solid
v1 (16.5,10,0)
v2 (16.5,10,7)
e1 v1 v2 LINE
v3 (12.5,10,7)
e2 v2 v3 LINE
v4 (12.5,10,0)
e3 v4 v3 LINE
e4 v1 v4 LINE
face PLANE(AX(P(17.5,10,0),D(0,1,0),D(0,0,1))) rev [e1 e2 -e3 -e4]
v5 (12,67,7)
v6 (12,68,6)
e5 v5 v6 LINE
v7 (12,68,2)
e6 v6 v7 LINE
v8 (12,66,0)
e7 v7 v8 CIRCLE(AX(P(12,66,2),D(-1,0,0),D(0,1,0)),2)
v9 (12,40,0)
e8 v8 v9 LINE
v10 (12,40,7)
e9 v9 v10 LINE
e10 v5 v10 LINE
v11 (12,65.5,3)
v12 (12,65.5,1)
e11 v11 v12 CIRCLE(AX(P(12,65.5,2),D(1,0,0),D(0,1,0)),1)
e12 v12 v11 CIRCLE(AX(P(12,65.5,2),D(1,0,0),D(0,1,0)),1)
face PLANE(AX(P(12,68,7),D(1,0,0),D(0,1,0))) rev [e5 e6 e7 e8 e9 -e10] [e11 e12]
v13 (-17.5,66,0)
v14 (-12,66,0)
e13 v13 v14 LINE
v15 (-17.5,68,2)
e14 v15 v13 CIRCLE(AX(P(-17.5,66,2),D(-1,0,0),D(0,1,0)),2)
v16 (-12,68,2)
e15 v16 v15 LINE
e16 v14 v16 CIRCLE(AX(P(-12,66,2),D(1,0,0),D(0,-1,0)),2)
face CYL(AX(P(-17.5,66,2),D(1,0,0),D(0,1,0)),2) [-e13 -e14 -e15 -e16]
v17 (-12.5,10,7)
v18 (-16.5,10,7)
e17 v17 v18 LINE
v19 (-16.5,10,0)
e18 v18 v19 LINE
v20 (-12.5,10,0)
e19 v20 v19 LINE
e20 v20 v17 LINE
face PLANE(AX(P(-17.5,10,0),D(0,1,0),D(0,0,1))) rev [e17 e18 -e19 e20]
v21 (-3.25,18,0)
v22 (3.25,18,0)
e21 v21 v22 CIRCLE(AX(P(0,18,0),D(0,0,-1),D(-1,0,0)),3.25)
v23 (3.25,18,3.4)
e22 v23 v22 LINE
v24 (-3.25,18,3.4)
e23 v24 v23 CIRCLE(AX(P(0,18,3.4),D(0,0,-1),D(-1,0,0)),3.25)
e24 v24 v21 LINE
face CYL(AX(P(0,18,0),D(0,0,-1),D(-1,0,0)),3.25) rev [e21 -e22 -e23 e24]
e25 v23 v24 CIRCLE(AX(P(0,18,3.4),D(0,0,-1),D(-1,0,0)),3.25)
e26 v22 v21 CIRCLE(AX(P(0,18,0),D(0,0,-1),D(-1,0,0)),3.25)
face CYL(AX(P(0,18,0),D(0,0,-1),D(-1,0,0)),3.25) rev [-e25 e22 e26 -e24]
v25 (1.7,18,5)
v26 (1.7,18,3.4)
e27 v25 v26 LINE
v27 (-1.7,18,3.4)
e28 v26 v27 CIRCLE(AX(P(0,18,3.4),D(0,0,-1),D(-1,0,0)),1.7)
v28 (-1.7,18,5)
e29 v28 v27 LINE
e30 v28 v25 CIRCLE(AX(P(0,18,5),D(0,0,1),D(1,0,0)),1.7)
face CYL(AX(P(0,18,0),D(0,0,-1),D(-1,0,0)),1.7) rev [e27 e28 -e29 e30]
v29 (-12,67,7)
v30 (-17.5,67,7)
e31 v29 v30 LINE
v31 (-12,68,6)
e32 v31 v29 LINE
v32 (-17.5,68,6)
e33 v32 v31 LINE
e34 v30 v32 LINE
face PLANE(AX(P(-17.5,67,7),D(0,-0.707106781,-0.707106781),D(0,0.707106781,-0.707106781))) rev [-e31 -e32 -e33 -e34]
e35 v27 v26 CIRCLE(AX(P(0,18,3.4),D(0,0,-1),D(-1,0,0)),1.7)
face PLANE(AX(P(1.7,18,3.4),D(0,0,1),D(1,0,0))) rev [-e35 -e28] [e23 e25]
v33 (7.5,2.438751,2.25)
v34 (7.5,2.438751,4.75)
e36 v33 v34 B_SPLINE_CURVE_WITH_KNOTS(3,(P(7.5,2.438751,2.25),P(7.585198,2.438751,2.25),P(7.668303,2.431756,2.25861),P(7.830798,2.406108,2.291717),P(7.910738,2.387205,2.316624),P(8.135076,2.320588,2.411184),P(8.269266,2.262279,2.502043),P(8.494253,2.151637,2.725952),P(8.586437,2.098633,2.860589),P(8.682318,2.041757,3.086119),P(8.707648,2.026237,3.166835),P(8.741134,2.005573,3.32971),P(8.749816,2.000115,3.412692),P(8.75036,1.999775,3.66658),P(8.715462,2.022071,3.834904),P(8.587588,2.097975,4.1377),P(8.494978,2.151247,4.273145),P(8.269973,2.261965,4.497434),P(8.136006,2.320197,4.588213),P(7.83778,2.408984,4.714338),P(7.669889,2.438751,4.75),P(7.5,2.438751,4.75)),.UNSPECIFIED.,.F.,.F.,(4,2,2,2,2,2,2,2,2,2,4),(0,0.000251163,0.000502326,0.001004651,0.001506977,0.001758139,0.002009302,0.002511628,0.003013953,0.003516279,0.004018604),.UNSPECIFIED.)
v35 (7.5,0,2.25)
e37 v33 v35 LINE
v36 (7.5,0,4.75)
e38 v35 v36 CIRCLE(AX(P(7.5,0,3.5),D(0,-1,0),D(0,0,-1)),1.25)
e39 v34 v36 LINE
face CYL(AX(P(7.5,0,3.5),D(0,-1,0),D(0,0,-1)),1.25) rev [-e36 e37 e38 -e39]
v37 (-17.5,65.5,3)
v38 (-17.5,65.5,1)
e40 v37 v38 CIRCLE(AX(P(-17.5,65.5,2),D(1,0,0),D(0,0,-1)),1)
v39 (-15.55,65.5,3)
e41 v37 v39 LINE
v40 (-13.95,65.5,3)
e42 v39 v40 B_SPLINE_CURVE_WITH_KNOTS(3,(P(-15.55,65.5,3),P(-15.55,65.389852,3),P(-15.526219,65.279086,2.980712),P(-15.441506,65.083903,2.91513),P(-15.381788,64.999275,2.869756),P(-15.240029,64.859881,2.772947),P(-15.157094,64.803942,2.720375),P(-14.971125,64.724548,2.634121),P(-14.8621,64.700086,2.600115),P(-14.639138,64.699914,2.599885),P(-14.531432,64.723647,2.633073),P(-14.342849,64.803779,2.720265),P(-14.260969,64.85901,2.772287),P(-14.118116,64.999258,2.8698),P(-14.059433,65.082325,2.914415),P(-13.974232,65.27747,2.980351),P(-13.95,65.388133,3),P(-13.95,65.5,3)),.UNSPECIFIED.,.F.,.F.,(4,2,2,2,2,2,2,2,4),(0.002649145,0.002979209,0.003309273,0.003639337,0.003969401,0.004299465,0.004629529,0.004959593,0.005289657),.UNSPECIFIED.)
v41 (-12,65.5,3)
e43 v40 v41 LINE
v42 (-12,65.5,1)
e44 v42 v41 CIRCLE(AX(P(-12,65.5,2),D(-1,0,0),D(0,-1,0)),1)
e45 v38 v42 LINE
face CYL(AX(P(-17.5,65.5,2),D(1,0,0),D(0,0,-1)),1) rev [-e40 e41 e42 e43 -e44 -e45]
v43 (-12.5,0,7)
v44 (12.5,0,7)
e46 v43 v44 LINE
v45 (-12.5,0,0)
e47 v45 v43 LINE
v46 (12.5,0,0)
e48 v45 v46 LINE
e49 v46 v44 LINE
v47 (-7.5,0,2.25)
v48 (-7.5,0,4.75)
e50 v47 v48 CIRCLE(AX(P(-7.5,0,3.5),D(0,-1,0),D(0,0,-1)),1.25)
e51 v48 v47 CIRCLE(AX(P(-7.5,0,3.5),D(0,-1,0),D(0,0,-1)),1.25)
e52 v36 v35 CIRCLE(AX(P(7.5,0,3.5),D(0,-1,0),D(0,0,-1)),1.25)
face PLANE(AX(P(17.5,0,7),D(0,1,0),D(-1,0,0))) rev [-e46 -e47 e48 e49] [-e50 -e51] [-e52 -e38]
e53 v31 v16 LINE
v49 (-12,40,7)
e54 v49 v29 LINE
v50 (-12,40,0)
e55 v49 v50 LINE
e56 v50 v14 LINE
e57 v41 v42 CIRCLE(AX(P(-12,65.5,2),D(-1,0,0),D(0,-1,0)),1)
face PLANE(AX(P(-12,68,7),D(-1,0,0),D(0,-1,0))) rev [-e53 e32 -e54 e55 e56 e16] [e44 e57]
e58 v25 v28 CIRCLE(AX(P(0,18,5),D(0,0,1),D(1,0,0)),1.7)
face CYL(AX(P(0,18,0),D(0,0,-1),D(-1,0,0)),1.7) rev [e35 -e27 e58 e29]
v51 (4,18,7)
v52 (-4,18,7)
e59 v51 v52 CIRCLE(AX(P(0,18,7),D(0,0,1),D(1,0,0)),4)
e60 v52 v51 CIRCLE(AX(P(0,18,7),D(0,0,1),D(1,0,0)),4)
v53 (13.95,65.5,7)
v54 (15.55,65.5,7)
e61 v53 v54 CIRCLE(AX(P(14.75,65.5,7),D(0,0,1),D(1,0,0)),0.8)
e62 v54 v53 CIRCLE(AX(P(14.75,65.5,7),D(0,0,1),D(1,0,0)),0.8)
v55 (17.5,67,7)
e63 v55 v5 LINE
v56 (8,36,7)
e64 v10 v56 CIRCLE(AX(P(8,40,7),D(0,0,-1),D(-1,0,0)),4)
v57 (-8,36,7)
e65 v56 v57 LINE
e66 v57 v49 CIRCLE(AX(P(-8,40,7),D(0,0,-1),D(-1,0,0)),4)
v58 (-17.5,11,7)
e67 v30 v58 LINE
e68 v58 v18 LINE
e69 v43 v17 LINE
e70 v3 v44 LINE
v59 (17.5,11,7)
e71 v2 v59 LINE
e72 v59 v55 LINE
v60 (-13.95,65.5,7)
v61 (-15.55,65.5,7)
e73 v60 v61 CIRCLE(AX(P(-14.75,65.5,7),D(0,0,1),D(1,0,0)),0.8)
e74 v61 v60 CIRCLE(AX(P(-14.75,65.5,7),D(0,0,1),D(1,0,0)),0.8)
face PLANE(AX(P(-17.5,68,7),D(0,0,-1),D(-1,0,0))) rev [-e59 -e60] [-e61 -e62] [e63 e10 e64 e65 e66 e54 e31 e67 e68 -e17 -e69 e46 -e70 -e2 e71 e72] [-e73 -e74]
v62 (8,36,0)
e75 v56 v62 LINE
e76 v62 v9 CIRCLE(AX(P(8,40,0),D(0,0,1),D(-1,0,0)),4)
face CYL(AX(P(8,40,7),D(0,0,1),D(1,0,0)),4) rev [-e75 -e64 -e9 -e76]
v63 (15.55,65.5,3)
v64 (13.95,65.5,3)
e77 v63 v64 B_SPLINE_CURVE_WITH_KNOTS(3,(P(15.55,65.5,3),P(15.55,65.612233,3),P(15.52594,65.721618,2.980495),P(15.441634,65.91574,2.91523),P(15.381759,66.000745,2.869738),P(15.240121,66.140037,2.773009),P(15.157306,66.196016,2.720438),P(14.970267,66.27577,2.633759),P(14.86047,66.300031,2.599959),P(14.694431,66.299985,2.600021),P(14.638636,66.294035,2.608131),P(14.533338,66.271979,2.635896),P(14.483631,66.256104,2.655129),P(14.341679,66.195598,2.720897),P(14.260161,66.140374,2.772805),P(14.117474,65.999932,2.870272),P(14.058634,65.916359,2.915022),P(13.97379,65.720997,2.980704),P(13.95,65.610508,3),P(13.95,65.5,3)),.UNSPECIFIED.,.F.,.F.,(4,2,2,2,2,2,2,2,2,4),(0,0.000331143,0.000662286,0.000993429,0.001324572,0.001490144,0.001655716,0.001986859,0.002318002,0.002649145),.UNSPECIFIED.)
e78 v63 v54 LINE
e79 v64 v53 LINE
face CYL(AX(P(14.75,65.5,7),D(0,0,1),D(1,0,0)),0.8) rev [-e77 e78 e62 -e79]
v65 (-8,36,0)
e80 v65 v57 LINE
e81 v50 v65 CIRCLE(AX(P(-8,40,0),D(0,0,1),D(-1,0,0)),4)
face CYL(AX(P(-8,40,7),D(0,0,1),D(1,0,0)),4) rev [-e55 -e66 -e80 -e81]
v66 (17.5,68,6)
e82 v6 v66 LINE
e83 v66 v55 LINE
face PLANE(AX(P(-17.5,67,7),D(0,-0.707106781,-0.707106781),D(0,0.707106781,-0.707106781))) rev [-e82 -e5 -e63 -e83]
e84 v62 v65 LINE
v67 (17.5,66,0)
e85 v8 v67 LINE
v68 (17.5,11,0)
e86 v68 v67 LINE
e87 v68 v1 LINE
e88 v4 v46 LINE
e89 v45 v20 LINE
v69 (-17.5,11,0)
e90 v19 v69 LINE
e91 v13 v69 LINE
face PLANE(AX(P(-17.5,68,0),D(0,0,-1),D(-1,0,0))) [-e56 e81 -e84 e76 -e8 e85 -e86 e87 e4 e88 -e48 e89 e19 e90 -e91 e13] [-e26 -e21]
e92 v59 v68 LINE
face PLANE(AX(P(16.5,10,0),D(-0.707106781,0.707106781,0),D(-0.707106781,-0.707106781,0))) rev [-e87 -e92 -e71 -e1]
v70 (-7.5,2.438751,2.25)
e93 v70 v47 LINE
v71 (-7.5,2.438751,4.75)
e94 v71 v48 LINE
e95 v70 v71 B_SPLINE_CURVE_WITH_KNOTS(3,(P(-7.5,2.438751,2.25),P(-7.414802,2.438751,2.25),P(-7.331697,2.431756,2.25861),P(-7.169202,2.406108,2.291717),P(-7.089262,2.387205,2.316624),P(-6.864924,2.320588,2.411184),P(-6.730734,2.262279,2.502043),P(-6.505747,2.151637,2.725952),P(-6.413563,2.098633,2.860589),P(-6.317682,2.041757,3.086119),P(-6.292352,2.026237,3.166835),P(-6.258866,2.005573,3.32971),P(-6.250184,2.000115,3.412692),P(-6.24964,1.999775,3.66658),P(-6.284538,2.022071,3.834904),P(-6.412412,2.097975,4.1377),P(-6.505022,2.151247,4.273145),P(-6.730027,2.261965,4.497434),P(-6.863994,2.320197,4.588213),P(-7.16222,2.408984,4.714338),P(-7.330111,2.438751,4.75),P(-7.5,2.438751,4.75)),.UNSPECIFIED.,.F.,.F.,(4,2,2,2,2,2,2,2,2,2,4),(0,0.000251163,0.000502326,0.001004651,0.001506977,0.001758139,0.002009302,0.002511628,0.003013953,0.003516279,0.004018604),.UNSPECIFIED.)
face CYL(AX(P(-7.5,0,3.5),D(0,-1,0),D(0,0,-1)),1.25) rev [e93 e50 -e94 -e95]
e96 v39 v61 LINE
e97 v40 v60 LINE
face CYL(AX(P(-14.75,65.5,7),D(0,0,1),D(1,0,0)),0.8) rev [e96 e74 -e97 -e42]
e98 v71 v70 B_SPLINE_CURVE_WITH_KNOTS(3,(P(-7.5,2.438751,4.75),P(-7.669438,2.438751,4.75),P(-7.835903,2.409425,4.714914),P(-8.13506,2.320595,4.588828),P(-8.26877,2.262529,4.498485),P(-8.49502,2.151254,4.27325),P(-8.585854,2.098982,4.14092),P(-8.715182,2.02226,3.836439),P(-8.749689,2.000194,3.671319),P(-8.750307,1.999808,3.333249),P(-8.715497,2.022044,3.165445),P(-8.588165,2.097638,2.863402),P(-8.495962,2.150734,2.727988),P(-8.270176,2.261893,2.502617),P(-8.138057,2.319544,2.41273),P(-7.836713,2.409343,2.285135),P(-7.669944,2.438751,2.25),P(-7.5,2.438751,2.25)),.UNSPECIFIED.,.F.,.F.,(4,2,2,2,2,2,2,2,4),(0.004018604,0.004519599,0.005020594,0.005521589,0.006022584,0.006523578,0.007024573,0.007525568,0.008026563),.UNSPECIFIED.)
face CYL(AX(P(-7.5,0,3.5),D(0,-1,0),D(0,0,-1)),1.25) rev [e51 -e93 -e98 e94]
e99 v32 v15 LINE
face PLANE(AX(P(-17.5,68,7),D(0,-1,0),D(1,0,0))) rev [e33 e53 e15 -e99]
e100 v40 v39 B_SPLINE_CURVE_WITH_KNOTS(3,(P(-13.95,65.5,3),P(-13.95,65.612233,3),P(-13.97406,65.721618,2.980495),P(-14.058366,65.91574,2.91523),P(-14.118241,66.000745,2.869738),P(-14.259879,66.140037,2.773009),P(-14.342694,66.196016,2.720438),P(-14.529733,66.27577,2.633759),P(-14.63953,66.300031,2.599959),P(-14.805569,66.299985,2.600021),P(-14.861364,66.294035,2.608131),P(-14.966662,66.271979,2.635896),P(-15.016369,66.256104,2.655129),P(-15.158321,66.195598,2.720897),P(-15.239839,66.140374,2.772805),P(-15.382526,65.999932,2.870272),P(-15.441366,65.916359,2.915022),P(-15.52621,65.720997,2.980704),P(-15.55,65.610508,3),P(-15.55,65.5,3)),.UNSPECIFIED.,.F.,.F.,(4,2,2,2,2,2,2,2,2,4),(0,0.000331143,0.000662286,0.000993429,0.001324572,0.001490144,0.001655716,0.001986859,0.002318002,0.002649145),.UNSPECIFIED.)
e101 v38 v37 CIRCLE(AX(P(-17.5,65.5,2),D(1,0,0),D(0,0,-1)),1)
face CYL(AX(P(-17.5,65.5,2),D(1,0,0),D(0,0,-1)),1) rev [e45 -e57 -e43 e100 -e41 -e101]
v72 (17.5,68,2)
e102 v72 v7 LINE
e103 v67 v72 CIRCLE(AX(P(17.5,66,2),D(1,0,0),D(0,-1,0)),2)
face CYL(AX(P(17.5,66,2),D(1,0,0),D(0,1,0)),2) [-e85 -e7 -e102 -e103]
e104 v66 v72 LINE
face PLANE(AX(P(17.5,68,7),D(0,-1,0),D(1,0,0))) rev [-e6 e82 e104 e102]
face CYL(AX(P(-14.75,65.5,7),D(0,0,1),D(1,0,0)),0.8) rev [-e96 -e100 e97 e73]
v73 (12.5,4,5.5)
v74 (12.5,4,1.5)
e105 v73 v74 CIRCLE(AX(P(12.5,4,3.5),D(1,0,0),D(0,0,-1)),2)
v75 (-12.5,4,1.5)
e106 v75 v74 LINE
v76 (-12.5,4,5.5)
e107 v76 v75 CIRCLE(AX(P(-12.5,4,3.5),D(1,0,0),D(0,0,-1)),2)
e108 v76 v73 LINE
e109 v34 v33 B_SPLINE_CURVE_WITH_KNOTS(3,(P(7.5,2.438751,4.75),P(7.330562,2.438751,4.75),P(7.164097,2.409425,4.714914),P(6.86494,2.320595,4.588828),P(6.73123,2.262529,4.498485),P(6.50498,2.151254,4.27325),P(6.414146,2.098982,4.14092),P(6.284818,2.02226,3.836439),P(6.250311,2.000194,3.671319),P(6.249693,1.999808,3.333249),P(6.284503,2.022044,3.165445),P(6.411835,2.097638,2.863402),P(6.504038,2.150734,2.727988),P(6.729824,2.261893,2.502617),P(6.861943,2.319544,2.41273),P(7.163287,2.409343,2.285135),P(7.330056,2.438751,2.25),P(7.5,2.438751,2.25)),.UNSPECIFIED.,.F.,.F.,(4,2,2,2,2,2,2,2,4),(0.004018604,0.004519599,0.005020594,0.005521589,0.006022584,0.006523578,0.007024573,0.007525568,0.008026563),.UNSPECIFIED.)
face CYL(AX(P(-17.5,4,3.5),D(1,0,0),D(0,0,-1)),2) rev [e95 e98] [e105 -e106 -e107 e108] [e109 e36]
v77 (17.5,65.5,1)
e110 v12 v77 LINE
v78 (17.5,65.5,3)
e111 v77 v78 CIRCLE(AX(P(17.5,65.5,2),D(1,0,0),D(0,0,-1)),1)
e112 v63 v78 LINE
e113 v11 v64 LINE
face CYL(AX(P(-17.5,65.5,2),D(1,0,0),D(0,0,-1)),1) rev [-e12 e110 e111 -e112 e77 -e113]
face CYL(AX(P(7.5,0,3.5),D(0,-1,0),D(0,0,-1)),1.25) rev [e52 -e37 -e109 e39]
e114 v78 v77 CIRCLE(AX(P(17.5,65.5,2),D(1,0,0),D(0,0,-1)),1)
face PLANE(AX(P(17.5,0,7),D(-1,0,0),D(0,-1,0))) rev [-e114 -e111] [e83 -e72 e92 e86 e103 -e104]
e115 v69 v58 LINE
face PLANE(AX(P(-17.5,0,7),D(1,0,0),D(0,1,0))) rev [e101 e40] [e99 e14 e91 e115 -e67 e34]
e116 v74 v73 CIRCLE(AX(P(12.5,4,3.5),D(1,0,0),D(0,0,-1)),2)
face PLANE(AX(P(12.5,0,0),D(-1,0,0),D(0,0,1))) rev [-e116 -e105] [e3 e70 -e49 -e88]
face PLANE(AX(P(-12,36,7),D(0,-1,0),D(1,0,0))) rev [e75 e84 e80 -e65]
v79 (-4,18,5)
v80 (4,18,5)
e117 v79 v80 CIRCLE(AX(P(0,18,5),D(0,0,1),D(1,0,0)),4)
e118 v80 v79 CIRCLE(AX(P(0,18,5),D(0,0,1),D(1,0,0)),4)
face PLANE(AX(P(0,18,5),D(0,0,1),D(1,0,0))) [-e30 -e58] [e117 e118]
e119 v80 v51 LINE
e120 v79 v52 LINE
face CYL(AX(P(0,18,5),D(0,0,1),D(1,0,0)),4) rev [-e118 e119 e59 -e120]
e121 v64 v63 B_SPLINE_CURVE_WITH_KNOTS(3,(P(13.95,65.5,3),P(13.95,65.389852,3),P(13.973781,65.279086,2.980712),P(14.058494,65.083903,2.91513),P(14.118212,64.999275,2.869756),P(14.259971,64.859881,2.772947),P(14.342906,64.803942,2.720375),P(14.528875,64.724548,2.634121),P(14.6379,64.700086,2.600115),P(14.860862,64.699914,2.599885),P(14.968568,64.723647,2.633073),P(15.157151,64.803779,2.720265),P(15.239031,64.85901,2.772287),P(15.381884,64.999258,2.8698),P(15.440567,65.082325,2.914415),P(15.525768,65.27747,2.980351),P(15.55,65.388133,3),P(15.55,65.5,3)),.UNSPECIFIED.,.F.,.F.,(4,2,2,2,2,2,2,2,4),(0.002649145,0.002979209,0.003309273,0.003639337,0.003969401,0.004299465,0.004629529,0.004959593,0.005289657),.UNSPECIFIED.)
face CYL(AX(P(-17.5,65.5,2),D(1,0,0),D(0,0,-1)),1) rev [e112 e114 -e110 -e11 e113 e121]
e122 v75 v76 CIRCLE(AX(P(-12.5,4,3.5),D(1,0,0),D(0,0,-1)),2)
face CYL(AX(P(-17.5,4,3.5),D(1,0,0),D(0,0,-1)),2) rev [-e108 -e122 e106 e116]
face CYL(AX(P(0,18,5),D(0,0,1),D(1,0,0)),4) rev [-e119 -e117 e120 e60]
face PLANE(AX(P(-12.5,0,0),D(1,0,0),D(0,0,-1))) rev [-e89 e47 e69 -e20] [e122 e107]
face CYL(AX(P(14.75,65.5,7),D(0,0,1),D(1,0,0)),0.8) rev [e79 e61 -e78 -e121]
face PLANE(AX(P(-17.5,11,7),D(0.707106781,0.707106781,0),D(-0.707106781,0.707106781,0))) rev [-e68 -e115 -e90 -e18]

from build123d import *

# Parameters (mm, degrees)
BOSS_EXTRUDE1_DEPTH                                 = 7
SKETCH2_R                                           = 1
CUT_EXTRUDE1_DEPTH                                  = 77.798437484
SKETCH3_W                                           = 5
SKETCH3_H                                           = 10
CUT_EXTRUDE2_DEPTH                                  = 71.563800918
SKETCH4_R                                           = 2
CUT_EXTRUDE3_DEPTH                                  = 75.652528423
M3_TAPPED_HOLE1_REACH                               = 72.564
M3_TAPPED_HOLE1_BORE_R                              = 1.25
FILLET1_R                                           = 4
CHAMFER1_SIZE                                       = 1
SKETCH8_R                                           = 4
CUT_EXTRUDE4_DEPTH                                  = 2
FILLET2_R                                           = 2
M2_TAPPED_HOLE1_D                                   = 1.6
M2_TAPPED_HOLE1_DEPTH                               = 5.2
M2_TAPPED_HOLE1_TIP                                 = 0.480688495
CBORE_FOR_M3_HEX_SOCKET_HEAD_CAP_SCREW1_D           = 3.4
CBORE_FOR_M3_HEX_SOCKET_HEAD_CAP_SCREW1_CBORE_D     = 6.5
CBORE_FOR_M3_HEX_SOCKET_HEAD_CAP_SCREW1_CBORE_DEPTH = 3.4


with BuildPart() as part:
    # Sketch1 → Boss-Extrude1 (new body)
    with BuildSketch(Plane.XY):
        Polygon((17.5, 0), (-17.5, 0), (-17.5, 68), (-12, 68), (-12, 36), (12, 36), (12, 68), (17.5, 68), align=None)
    extrude(amount=BOSS_EXTRUDE1_DEPTH)

    # Sketch2 → Cut-Extrude1 (cut, through all)
    with BuildSketch(Plane(origin=(17.5, 0, 0), x_dir=(0, 0, -1), z_dir=(1, 0, 0))):
        with Locations((-2, 65.5)):
            Circle(SKETCH2_R)
    extrude(amount=-CUT_EXTRUDE1_DEPTH, mode=Mode.SUBTRACT)

    # Sketch3 → Cut-Extrude2 (cut, through all)
    with BuildSketch(Plane.XY.offset(7)):
        with Locations((-15, 5)):
            Rectangle(SKETCH3_W, SKETCH3_H)
        with Locations((15, 5)):
            Rectangle(SKETCH3_W, SKETCH3_H)
    extrude(amount=-CUT_EXTRUDE2_DEPTH, mode=Mode.SUBTRACT)

    # Sketch4 → Cut-Extrude3 (cut, through all)
    with BuildSketch(Plane(origin=(12.5, 0, 0), x_dir=(0, 0, -1), z_dir=(1, 0, 0))):
        with Locations((-3.5, 4)):
            Circle(SKETCH4_R)
    extrude(amount=-CUT_EXTRUDE3_DEPTH, mode=Mode.SUBTRACT)

    # M3 Tapped Hole1 bore → M3 Tapped Hole1 (cut, up to next)
    with BuildSketch(Plane.XZ, mode=Mode.PRIVATE) as m3_tapped_hole1_sk1:
        with Locations((7.5, 3.5)):
            Circle(M3_TAPPED_HOLE1_BORE_R)
    m3_tapped_hole1_tool1 = extrude(m3_tapped_hole1_sk1.sketch, amount=-M3_TAPPED_HOLE1_REACH, mode=Mode.PRIVATE) & part.part
    # M3 Tapped Hole1 bore → M3 Tapped Hole1 (cut, up to next)
    with BuildSketch(Plane.XZ, mode=Mode.PRIVATE) as m3_tapped_hole1_sk2:
        with Locations((-7.5, 3.5)):
            Circle(M3_TAPPED_HOLE1_BORE_R)
    m3_tapped_hole1_tool2 = extrude(m3_tapped_hole1_sk2.sketch, amount=-M3_TAPPED_HOLE1_REACH, mode=Mode.PRIVATE) & part.part
    add(m3_tapped_hole1_tool1.solids().sort_by_distance((7.5, 0, 3.5))[0], mode=Mode.SUBTRACT)
    add(m3_tapped_hole1_tool2.solids().sort_by_distance((-7.5, 0, 3.5))[0], mode=Mode.SUBTRACT)

    # Fillet1
    fillet1_edges = [part.edges().sort_by_distance(p)[0] for p in [
        (-12, 36, 3.5),
        (12, 36, 3.5),
    ]]
    fillet(fillet1_edges, radius=FILLET1_R)

    # Chamfer1
    chamfer1_edges = [part.edges().sort_by_distance(p)[0] for p in [
        (14.75, 68, 7),
        (-14.75, 68, 7),
        (-17.5, 10, 3.5),
        (17.5, 10, 3.5),
    ]]
    chamfer(chamfer1_edges, length=CHAMFER1_SIZE)

    # Sketch8 → Cut-Extrude4 (cut)
    with BuildSketch(Plane.XY.offset(7)):
        with Locations((0, 18)):
            Circle(SKETCH8_R)
    extrude(amount=-CUT_EXTRUDE4_DEPTH, mode=Mode.SUBTRACT)

    # Fillet2
    fillet2_edges = [part.edges().sort_by_distance(p)[0] for p in [
        (-14.75, 68, 0),
        (14.75, 68, 0),
    ]]
    fillet(fillet2_edges, radius=FILLET2_R)

    # M2 Tapped Hole1
    with Locations(Plane.XY.offset(7)):
        with Locations((-14.75, 65.5), (14.75, 65.5)):
            Hole(M2_TAPPED_HOLE1_D / 2, depth=M2_TAPPED_HOLE1_DEPTH)
            with Locations((0, 0, -(M2_TAPPED_HOLE1_DEPTH + M2_TAPPED_HOLE1_TIP / 2))):  # 118° drill point
                Cone(0, M2_TAPPED_HOLE1_D / 2, M2_TAPPED_HOLE1_TIP, mode=Mode.SUBTRACT)

    # CBORE for M3 Hex Socket Head Cap Screw1 (through all)
    with Locations(Plane(origin=(0, 0, 0), x_dir=(-1, 0, 0), z_dir=(0, 0, -1))):
        with Locations((0, 18)):
            CounterBoreHole(CBORE_FOR_M3_HEX_SOCKET_HEAD_CAP_SCREW1_D / 2, CBORE_FOR_M3_HEX_SOCKET_HEAD_CAP_SCREW1_CBORE_D / 2, CBORE_FOR_M3_HEX_SOCKET_HEAD_CAP_SCREW1_CBORE_DEPTH)


solid = part.part
